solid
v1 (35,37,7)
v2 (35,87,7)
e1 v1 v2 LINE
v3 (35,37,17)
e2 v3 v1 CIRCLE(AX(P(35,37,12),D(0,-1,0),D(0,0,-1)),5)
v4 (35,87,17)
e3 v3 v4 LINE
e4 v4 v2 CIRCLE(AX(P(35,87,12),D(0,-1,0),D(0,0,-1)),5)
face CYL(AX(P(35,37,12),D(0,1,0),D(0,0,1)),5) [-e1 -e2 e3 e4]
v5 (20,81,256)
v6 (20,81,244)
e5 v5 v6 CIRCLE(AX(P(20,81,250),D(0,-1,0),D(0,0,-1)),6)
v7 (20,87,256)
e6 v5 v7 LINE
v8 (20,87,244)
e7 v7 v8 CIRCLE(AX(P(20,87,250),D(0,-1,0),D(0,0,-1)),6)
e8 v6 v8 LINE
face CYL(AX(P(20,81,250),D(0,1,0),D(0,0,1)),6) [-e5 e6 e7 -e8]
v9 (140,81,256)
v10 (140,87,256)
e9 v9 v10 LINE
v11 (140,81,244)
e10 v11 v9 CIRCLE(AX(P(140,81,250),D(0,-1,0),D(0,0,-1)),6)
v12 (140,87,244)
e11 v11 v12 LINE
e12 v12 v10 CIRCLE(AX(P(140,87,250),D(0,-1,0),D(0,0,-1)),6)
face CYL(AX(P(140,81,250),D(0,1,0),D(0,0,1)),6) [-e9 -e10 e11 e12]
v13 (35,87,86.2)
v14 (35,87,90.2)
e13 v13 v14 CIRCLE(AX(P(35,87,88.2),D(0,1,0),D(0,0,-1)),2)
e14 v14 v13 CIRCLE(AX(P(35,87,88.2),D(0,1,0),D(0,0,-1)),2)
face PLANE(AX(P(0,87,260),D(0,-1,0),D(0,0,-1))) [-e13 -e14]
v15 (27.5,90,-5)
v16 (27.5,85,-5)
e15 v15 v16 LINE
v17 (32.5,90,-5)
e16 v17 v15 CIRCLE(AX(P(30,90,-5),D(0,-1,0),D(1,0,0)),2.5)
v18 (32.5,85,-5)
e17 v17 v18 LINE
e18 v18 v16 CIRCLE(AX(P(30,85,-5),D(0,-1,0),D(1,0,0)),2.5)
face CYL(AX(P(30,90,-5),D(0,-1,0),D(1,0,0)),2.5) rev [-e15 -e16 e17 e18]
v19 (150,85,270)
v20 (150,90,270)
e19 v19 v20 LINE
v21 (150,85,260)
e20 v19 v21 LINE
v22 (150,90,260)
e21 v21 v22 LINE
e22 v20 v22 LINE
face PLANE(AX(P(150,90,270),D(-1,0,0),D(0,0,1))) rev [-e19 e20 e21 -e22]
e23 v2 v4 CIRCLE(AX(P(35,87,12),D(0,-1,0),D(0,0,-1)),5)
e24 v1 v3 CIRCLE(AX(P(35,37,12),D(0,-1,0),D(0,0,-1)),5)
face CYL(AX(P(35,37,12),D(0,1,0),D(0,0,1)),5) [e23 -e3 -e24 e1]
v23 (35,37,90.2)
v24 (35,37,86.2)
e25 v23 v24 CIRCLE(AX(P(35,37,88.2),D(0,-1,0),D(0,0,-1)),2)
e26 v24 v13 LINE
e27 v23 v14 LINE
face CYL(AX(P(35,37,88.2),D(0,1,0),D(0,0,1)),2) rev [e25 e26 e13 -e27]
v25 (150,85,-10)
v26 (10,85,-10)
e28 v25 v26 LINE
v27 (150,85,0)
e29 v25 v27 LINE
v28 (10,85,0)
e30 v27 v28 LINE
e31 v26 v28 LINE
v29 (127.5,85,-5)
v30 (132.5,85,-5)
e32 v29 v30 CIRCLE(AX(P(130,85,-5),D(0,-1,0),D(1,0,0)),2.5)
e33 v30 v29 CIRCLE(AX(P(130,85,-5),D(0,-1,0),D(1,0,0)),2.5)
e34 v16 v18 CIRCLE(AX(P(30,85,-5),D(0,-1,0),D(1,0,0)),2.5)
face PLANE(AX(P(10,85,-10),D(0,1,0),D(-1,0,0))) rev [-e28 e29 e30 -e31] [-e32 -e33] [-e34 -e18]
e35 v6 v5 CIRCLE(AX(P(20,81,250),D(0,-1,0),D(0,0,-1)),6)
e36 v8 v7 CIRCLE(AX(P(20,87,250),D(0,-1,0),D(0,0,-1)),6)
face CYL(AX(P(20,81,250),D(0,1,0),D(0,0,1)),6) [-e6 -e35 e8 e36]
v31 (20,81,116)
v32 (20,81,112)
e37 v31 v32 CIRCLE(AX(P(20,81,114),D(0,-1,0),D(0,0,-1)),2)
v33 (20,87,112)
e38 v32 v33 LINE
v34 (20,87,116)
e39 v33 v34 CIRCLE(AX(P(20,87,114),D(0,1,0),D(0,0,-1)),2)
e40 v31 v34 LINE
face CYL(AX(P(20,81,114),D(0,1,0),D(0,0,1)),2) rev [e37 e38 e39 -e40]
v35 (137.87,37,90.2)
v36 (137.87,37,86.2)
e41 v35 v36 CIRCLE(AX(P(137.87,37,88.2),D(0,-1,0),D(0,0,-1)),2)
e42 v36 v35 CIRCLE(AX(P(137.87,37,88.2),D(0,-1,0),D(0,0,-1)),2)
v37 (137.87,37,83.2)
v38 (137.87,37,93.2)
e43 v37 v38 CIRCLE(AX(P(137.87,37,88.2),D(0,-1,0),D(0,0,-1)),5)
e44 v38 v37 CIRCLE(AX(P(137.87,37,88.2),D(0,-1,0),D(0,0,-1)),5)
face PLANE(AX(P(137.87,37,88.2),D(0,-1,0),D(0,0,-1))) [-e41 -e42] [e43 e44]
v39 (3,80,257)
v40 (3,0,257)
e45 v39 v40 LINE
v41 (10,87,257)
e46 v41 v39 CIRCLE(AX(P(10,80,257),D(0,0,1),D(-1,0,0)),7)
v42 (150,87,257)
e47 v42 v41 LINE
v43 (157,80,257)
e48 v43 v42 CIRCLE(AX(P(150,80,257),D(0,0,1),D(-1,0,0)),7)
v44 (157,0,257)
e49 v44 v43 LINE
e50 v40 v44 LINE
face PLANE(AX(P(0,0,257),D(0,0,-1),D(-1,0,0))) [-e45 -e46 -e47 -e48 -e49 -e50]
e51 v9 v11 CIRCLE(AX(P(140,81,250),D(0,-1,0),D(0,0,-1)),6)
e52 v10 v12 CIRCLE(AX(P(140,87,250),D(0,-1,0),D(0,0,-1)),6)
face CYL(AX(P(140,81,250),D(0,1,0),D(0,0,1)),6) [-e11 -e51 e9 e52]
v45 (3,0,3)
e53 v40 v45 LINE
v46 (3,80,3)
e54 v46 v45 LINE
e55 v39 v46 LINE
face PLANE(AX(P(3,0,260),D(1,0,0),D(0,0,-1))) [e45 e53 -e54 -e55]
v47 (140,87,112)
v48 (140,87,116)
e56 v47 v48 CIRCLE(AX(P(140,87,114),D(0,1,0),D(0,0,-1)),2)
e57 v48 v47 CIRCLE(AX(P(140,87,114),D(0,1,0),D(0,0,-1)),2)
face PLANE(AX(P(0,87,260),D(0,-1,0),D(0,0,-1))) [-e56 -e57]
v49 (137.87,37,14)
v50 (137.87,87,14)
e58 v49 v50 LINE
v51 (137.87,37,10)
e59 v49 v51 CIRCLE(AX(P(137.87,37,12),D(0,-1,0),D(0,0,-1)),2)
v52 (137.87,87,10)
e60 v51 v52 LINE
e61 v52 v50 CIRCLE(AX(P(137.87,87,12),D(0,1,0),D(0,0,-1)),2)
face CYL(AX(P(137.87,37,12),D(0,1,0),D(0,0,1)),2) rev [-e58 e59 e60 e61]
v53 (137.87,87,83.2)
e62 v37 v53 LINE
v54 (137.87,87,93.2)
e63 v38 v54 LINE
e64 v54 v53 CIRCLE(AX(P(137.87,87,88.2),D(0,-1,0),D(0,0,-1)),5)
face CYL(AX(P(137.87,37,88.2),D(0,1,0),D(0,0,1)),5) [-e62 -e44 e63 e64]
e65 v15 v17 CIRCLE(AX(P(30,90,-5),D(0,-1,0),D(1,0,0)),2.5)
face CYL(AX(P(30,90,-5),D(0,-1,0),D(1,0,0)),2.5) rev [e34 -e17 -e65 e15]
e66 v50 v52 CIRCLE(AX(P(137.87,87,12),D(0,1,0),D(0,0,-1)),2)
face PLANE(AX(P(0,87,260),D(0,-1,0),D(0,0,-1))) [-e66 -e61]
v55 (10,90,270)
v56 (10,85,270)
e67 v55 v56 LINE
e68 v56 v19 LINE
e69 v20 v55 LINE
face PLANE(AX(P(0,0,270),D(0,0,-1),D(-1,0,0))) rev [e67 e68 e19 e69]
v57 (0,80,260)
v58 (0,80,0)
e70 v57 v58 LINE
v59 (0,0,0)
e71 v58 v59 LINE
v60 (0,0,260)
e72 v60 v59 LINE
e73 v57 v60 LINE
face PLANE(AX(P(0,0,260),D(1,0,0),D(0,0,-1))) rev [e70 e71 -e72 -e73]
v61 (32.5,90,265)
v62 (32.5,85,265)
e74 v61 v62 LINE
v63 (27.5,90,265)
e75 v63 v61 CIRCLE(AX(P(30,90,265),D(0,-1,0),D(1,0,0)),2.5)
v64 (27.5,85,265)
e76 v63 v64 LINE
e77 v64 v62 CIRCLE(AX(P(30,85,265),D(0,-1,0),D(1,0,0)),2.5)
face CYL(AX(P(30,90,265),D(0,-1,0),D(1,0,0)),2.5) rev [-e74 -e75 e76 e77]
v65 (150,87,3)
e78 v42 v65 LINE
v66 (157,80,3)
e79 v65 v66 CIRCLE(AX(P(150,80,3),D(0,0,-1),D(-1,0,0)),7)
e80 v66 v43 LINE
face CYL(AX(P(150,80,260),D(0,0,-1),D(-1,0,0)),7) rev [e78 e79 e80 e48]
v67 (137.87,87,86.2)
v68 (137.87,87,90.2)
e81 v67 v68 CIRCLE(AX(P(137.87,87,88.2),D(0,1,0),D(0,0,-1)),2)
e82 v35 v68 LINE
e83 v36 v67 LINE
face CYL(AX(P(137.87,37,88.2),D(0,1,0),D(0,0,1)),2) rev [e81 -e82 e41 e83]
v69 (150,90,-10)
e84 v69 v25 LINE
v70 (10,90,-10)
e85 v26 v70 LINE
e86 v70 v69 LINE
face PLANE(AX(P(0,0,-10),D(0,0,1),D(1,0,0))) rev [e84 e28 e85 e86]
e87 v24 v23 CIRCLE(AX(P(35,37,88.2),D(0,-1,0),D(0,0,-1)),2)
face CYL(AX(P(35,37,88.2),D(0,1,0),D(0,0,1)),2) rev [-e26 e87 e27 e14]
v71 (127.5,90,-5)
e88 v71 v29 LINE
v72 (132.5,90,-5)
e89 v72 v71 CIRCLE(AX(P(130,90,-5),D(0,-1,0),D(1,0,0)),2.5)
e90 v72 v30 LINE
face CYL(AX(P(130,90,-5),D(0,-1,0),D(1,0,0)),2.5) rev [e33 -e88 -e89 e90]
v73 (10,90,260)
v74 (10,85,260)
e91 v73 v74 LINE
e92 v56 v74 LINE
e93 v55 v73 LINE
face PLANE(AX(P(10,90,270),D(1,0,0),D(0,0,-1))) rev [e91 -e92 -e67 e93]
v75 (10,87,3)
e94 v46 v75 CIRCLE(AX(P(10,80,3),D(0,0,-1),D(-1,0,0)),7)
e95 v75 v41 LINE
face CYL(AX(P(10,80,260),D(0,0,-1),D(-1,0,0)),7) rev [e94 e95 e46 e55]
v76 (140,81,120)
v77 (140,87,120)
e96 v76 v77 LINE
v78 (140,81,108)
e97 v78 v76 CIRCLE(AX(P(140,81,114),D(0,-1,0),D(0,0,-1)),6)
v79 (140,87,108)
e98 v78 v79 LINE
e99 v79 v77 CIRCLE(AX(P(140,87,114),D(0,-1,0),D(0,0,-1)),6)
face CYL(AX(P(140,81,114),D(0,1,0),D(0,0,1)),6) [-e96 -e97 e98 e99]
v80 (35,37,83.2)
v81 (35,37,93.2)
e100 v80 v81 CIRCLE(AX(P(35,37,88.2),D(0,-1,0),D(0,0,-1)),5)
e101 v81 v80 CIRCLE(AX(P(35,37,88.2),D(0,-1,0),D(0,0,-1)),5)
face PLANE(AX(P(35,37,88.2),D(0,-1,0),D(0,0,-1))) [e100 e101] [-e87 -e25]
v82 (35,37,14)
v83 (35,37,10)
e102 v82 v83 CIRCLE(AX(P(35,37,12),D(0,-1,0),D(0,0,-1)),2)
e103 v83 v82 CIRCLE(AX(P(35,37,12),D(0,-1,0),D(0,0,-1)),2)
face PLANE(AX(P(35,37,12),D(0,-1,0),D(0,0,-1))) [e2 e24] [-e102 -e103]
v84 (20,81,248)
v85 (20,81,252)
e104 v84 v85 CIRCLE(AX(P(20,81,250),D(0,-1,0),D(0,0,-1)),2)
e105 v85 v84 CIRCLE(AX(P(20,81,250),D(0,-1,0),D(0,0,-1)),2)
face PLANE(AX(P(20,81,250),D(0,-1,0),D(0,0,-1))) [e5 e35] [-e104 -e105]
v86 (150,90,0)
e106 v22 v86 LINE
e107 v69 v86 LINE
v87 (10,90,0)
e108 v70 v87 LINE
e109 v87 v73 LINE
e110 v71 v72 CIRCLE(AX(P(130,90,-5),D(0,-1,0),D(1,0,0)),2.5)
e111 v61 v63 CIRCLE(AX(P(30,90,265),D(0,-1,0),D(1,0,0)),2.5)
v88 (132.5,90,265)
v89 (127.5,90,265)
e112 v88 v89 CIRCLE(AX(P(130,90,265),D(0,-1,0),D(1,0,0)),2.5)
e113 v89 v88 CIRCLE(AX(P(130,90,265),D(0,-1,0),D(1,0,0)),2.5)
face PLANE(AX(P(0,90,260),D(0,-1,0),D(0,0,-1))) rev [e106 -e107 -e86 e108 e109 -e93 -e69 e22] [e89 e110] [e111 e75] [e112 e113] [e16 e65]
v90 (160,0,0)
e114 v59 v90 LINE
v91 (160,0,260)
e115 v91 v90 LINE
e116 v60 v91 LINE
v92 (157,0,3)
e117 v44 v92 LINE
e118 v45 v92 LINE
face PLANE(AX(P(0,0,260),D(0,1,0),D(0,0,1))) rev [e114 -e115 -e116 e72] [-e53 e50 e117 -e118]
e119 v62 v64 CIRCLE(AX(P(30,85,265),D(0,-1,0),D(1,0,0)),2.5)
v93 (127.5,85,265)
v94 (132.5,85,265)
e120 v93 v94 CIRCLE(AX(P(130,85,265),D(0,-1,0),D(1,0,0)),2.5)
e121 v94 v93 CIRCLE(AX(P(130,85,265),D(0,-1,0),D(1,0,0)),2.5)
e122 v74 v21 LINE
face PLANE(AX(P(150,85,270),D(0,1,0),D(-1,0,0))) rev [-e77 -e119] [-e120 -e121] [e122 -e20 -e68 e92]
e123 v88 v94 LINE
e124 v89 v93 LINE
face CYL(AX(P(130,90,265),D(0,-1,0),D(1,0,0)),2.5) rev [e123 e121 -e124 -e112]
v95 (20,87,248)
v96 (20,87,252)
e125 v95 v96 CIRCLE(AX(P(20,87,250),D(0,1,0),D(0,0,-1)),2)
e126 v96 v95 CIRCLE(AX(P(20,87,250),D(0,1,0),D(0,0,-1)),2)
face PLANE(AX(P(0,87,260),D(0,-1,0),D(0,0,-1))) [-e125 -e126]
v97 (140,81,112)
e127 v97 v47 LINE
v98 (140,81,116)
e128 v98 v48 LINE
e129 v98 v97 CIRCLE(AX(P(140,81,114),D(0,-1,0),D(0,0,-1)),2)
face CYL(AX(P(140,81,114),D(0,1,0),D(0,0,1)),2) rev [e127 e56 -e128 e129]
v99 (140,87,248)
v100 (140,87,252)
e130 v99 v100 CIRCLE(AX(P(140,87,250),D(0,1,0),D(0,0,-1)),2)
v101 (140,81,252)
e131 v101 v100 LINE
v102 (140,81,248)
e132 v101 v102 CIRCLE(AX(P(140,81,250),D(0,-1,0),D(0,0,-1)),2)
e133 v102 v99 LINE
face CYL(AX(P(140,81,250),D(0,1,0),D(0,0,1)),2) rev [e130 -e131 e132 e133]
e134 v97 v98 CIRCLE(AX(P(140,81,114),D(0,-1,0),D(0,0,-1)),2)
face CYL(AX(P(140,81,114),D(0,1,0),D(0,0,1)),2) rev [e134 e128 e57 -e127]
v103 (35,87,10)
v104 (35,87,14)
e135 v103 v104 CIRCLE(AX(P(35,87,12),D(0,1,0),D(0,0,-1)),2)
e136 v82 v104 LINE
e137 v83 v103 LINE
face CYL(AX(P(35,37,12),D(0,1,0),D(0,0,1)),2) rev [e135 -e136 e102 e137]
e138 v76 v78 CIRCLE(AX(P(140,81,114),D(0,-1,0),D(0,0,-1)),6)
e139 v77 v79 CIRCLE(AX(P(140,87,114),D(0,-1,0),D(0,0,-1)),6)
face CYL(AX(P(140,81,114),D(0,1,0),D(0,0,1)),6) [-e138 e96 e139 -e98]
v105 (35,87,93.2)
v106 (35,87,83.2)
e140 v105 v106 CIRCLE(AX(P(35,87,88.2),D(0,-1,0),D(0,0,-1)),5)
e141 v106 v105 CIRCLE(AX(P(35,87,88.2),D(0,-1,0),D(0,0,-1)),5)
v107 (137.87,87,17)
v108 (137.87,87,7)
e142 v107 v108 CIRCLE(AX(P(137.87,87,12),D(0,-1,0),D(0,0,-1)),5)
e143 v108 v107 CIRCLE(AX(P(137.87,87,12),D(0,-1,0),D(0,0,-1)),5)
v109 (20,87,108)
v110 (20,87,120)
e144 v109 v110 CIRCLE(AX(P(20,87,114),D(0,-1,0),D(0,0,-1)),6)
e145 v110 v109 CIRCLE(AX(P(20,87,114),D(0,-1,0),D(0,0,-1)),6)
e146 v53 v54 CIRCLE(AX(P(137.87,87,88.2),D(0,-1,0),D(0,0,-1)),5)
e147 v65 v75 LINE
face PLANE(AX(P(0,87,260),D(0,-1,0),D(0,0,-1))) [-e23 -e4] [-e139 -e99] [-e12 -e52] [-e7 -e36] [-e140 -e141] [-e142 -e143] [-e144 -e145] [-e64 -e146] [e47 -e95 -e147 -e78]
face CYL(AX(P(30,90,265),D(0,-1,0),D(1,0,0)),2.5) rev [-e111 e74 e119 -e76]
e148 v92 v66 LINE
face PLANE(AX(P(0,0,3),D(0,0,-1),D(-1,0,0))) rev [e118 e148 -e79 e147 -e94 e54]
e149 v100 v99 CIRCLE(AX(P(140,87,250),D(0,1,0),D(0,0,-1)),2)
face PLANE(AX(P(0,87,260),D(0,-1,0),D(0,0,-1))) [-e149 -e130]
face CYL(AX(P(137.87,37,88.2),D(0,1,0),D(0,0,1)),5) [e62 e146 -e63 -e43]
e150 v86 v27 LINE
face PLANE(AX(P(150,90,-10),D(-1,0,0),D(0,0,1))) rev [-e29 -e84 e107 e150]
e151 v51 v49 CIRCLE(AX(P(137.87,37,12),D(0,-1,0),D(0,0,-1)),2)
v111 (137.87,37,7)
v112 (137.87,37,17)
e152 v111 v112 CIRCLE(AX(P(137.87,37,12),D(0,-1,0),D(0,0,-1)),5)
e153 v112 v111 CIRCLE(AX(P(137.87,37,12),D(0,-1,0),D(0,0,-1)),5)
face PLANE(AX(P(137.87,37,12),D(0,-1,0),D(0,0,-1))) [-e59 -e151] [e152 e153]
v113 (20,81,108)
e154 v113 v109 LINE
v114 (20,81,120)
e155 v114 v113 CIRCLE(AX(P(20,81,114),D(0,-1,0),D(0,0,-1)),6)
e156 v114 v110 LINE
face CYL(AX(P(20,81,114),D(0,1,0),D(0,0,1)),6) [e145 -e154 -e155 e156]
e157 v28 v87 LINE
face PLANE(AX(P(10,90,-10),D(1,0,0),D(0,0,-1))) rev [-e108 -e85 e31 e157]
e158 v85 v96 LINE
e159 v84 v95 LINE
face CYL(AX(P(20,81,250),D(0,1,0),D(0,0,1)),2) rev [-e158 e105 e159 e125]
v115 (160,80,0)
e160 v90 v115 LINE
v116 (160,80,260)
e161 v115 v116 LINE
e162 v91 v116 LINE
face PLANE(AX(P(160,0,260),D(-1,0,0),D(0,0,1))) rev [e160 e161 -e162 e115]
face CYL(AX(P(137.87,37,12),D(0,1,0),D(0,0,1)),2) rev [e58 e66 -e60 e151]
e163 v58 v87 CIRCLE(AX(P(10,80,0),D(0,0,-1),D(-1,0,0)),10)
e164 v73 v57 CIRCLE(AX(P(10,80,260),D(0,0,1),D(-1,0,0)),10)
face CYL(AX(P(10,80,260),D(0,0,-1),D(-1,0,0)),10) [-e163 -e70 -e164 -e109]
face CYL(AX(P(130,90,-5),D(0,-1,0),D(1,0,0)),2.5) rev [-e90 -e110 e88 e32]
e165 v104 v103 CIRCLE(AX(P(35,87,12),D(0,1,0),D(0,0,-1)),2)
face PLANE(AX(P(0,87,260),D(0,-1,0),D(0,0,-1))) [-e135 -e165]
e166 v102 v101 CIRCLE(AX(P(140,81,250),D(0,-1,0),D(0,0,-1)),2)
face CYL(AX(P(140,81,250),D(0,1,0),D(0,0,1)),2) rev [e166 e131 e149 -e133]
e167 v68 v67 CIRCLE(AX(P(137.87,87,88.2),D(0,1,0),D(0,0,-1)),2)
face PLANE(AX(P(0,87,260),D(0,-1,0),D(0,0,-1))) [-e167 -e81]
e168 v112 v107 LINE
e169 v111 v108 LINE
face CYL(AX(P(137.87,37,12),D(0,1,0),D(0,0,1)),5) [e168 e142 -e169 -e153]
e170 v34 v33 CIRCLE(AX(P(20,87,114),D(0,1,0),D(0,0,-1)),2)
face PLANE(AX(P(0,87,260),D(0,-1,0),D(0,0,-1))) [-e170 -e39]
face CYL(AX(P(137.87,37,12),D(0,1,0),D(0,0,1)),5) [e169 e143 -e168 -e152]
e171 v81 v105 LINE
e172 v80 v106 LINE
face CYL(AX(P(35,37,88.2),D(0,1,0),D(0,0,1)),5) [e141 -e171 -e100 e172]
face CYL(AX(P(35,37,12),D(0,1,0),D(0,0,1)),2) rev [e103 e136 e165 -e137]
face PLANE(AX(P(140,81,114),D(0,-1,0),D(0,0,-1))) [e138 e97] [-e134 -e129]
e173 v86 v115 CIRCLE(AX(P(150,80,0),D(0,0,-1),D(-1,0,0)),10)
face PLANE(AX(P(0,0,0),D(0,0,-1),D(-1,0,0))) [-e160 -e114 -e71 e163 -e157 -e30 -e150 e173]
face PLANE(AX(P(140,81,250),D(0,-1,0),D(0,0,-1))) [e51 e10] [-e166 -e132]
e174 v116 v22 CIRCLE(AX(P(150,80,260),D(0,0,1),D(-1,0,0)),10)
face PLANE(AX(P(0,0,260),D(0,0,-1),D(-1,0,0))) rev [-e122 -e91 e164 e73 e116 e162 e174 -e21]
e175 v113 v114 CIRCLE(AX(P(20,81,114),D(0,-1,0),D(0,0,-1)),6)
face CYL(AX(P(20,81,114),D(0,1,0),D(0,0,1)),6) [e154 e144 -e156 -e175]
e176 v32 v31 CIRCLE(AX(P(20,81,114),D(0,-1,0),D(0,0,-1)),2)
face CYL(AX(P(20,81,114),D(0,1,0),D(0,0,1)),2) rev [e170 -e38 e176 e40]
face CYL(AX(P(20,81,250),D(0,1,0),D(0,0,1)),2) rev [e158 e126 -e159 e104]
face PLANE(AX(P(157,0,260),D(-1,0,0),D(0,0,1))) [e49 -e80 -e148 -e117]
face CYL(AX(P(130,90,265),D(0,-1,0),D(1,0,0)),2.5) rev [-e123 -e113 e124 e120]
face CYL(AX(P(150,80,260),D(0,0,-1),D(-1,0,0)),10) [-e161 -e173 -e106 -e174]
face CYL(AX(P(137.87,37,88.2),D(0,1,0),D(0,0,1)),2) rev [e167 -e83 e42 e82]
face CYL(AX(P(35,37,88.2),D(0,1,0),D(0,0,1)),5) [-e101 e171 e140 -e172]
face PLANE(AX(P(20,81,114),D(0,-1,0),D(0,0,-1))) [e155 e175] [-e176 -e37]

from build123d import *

# Parameters (mm, degrees)
SKETCH1_W           = 160
SKETCH1_H           = 90
BOSS_EXTRUDE1_DEPTH = 260
FILLET2_R           = 10
SHELL1_T            = -3
SKETCH2_R           = 5
SKETCH2_R_2         = 2
BOSS_EXTRUDE2_DEPTH = 50
SKETCH3_R           = 6
SKETCH3_R_2         = 2
BOSS_EXTRUDE3_DEPTH = 6
SKETCH4_W           = 140
SKETCH4_H           = 5
BOSS_EXTRUDE4_DEPTH = 10
SKETCH5_W           = 140
SKETCH5_H           = 5
BOSS_EXTRUDE5_DEPTH = 10
SKETCH6_R           = 2.5
CUT_EXTRUDE1_DEPTH  = 326.153809758


with BuildPart() as part:
    # Sketch1 → Boss-Extrude1 (new body)
    with BuildSketch(Plane.XY):
        with Locations((80, 45)):
            Rectangle(SKETCH1_W, SKETCH1_H)
    extrude(amount=BOSS_EXTRUDE1_DEPTH)

    # Fillet2
    fillet2_edges = [part.edges().sort_by_distance(p)[0] for p in [
        (0, 90, 130),
        (160, 90, 130),
    ]]
    fillet(fillet2_edges, radius=FILLET2_R)

    # Shell1
    shell1_openings = [part.faces().sort_by_distance(p)[0] for p in [
        (80, 0, 130),
    ]]
    offset(amount=SHELL1_T, openings=shell1_openings, kind=Kind.INTERSECTION)

    # Sketch2 → Boss-Extrude2 (add)
    # profile 1 of 4: a face of its own
    with BuildSketch(Plane(origin=(0, 87, 0), x_dir=(-1, 0, 0), z_dir=(0, -1, 0))):
        with Locations(Location((-35, -88.2, 0), (0, 0, 90))):
            Circle(SKETCH2_R)
        with Locations(Location((-35, -88.2, 0), (0, 0, 90))):
            Circle(SKETCH2_R_2, mode=Mode.SUBTRACT)
    # profile 2 of 4: a face of its own
    with BuildSketch(Plane(origin=(0, 87, 0), x_dir=(-1, 0, 0), z_dir=(0, -1, 0))):
        with Locations(Location((-35, -12, 0), (0, 0, 90))):
            Circle(SKETCH2_R)
        with Locations(Location((-35, -12, 0), (0, 0, 90))):
            Circle(SKETCH2_R_2, mode=Mode.SUBTRACT)
    # profile 3 of 4: a face of its own
    with BuildSketch(Plane(origin=(0, 87, 0), x_dir=(-1, 0, 0), z_dir=(0, -1, 0))):
        with Locations(Location((-137.87, -12, 0), (0, 0, 90))):
            Circle(SKETCH2_R)
        with Locations(Location((-137.87, -12, 0), (0, 0, 90))):
            Circle(SKETCH2_R_2, mode=Mode.SUBTRACT)
    # profile 4 of 4: a face of its own
    with BuildSketch(Plane(origin=(0, 87, 0), x_dir=(-1, 0, 0), z_dir=(0, -1, 0))):
        with Locations(Location((-137.87, -88.2, 0), (0, 0, 90))):
            Circle(SKETCH2_R)
        with Locations(Location((-137.87, -88.2, 0), (0, 0, 90))):
            Circle(SKETCH2_R_2, mode=Mode.SUBTRACT)
    extrude(amount=BOSS_EXTRUDE2_DEPTH)

    # Sketch3 → Boss-Extrude3 (add)
    # profile 1 of 4: a face of its own
    with BuildSketch(Plane(origin=(0, 87, 0), x_dir=(-1, 0, 0), z_dir=(0, -1, 0))):
        with Locations(Location((-20, -114, 0), (0, 0, 90))):
            Circle(SKETCH3_R)
        with Locations(Location((-20, -114, 0), (0, 0, 90))):
            Circle(SKETCH3_R_2, mode=Mode.SUBTRACT)
    # profile 2 of 4: a face of its own
    with BuildSketch(Plane(origin=(0, 87, 0), x_dir=(-1, 0, 0), z_dir=(0, -1, 0))):
        with Locations(Location((-20, -250, 0), (0, 0, 90))):
            Circle(SKETCH3_R)
        with Locations(Location((-20, -250, 0), (0, 0, 90))):
            Circle(SKETCH3_R_2, mode=Mode.SUBTRACT)
    # profile 3 of 4: a face of its own
    with BuildSketch(Plane(origin=(0, 87, 0), x_dir=(-1, 0, 0), z_dir=(0, -1, 0))):
        with Locations(Location((-140, -114, 0), (0, 0, 90))):
            Circle(SKETCH3_R)
        with Locations(Location((-140, -114, 0), (0, 0, 90))):
            Circle(SKETCH3_R_2, mode=Mode.SUBTRACT)
    # profile 4 of 4: a face of its own
    with BuildSketch(Plane(origin=(0, 87, 0), x_dir=(-1, 0, 0), z_dir=(0, -1, 0))):
        with Locations(Location((-140, -250, 0), (0, 0, 90))):
            Circle(SKETCH3_R)
        with Locations(Location((-140, -250, 0), (0, 0, 90))):
            Circle(SKETCH3_R_2, mode=Mode.SUBTRACT)
    extrude(amount=BOSS_EXTRUDE3_DEPTH)

    # Sketch4 → Boss-Extrude4 (add)
    with BuildSketch(Plane(origin=(0, 0, 0), x_dir=(-1, 0, 0), z_dir=(0, 0, -1))):
        with Locations((-80, 87.5)):
            Rectangle(SKETCH4_W, SKETCH4_H)
    extrude(amount=BOSS_EXTRUDE4_DEPTH)

    # Sketch5 → Boss-Extrude5 (add)
    with BuildSketch(Plane.XY.offset(260)):
        with Locations((80, 87.5)):
            Rectangle(SKETCH5_W, SKETCH5_H)
    extrude(amount=BOSS_EXTRUDE5_DEPTH)

    # Sketch6 → Cut-Extrude1 (cut, through all)
    with BuildSketch(Plane(origin=(0, 85, 0), x_dir=(-1, 0, 0), z_dir=(0, -1, 0))):
        with Locations(Location((-130, -265, 0), (0, 0, 180))):
            Circle(SKETCH6_R)
        with Locations(Location((-30, -265, 0), (0, 0, 180))):
            Circle(SKETCH6_R)
        with Locations(Location((-130, 5, 0), (0, 0, 180))):
            Circle(SKETCH6_R)
        with Locations(Location((-30, 5, 0), (0, 0, 180))):
            Circle(SKETCH6_R)
    extrude(amount=-CUT_EXTRUDE1_DEPTH, mode=Mode.SUBTRACT)


solid = part.part
